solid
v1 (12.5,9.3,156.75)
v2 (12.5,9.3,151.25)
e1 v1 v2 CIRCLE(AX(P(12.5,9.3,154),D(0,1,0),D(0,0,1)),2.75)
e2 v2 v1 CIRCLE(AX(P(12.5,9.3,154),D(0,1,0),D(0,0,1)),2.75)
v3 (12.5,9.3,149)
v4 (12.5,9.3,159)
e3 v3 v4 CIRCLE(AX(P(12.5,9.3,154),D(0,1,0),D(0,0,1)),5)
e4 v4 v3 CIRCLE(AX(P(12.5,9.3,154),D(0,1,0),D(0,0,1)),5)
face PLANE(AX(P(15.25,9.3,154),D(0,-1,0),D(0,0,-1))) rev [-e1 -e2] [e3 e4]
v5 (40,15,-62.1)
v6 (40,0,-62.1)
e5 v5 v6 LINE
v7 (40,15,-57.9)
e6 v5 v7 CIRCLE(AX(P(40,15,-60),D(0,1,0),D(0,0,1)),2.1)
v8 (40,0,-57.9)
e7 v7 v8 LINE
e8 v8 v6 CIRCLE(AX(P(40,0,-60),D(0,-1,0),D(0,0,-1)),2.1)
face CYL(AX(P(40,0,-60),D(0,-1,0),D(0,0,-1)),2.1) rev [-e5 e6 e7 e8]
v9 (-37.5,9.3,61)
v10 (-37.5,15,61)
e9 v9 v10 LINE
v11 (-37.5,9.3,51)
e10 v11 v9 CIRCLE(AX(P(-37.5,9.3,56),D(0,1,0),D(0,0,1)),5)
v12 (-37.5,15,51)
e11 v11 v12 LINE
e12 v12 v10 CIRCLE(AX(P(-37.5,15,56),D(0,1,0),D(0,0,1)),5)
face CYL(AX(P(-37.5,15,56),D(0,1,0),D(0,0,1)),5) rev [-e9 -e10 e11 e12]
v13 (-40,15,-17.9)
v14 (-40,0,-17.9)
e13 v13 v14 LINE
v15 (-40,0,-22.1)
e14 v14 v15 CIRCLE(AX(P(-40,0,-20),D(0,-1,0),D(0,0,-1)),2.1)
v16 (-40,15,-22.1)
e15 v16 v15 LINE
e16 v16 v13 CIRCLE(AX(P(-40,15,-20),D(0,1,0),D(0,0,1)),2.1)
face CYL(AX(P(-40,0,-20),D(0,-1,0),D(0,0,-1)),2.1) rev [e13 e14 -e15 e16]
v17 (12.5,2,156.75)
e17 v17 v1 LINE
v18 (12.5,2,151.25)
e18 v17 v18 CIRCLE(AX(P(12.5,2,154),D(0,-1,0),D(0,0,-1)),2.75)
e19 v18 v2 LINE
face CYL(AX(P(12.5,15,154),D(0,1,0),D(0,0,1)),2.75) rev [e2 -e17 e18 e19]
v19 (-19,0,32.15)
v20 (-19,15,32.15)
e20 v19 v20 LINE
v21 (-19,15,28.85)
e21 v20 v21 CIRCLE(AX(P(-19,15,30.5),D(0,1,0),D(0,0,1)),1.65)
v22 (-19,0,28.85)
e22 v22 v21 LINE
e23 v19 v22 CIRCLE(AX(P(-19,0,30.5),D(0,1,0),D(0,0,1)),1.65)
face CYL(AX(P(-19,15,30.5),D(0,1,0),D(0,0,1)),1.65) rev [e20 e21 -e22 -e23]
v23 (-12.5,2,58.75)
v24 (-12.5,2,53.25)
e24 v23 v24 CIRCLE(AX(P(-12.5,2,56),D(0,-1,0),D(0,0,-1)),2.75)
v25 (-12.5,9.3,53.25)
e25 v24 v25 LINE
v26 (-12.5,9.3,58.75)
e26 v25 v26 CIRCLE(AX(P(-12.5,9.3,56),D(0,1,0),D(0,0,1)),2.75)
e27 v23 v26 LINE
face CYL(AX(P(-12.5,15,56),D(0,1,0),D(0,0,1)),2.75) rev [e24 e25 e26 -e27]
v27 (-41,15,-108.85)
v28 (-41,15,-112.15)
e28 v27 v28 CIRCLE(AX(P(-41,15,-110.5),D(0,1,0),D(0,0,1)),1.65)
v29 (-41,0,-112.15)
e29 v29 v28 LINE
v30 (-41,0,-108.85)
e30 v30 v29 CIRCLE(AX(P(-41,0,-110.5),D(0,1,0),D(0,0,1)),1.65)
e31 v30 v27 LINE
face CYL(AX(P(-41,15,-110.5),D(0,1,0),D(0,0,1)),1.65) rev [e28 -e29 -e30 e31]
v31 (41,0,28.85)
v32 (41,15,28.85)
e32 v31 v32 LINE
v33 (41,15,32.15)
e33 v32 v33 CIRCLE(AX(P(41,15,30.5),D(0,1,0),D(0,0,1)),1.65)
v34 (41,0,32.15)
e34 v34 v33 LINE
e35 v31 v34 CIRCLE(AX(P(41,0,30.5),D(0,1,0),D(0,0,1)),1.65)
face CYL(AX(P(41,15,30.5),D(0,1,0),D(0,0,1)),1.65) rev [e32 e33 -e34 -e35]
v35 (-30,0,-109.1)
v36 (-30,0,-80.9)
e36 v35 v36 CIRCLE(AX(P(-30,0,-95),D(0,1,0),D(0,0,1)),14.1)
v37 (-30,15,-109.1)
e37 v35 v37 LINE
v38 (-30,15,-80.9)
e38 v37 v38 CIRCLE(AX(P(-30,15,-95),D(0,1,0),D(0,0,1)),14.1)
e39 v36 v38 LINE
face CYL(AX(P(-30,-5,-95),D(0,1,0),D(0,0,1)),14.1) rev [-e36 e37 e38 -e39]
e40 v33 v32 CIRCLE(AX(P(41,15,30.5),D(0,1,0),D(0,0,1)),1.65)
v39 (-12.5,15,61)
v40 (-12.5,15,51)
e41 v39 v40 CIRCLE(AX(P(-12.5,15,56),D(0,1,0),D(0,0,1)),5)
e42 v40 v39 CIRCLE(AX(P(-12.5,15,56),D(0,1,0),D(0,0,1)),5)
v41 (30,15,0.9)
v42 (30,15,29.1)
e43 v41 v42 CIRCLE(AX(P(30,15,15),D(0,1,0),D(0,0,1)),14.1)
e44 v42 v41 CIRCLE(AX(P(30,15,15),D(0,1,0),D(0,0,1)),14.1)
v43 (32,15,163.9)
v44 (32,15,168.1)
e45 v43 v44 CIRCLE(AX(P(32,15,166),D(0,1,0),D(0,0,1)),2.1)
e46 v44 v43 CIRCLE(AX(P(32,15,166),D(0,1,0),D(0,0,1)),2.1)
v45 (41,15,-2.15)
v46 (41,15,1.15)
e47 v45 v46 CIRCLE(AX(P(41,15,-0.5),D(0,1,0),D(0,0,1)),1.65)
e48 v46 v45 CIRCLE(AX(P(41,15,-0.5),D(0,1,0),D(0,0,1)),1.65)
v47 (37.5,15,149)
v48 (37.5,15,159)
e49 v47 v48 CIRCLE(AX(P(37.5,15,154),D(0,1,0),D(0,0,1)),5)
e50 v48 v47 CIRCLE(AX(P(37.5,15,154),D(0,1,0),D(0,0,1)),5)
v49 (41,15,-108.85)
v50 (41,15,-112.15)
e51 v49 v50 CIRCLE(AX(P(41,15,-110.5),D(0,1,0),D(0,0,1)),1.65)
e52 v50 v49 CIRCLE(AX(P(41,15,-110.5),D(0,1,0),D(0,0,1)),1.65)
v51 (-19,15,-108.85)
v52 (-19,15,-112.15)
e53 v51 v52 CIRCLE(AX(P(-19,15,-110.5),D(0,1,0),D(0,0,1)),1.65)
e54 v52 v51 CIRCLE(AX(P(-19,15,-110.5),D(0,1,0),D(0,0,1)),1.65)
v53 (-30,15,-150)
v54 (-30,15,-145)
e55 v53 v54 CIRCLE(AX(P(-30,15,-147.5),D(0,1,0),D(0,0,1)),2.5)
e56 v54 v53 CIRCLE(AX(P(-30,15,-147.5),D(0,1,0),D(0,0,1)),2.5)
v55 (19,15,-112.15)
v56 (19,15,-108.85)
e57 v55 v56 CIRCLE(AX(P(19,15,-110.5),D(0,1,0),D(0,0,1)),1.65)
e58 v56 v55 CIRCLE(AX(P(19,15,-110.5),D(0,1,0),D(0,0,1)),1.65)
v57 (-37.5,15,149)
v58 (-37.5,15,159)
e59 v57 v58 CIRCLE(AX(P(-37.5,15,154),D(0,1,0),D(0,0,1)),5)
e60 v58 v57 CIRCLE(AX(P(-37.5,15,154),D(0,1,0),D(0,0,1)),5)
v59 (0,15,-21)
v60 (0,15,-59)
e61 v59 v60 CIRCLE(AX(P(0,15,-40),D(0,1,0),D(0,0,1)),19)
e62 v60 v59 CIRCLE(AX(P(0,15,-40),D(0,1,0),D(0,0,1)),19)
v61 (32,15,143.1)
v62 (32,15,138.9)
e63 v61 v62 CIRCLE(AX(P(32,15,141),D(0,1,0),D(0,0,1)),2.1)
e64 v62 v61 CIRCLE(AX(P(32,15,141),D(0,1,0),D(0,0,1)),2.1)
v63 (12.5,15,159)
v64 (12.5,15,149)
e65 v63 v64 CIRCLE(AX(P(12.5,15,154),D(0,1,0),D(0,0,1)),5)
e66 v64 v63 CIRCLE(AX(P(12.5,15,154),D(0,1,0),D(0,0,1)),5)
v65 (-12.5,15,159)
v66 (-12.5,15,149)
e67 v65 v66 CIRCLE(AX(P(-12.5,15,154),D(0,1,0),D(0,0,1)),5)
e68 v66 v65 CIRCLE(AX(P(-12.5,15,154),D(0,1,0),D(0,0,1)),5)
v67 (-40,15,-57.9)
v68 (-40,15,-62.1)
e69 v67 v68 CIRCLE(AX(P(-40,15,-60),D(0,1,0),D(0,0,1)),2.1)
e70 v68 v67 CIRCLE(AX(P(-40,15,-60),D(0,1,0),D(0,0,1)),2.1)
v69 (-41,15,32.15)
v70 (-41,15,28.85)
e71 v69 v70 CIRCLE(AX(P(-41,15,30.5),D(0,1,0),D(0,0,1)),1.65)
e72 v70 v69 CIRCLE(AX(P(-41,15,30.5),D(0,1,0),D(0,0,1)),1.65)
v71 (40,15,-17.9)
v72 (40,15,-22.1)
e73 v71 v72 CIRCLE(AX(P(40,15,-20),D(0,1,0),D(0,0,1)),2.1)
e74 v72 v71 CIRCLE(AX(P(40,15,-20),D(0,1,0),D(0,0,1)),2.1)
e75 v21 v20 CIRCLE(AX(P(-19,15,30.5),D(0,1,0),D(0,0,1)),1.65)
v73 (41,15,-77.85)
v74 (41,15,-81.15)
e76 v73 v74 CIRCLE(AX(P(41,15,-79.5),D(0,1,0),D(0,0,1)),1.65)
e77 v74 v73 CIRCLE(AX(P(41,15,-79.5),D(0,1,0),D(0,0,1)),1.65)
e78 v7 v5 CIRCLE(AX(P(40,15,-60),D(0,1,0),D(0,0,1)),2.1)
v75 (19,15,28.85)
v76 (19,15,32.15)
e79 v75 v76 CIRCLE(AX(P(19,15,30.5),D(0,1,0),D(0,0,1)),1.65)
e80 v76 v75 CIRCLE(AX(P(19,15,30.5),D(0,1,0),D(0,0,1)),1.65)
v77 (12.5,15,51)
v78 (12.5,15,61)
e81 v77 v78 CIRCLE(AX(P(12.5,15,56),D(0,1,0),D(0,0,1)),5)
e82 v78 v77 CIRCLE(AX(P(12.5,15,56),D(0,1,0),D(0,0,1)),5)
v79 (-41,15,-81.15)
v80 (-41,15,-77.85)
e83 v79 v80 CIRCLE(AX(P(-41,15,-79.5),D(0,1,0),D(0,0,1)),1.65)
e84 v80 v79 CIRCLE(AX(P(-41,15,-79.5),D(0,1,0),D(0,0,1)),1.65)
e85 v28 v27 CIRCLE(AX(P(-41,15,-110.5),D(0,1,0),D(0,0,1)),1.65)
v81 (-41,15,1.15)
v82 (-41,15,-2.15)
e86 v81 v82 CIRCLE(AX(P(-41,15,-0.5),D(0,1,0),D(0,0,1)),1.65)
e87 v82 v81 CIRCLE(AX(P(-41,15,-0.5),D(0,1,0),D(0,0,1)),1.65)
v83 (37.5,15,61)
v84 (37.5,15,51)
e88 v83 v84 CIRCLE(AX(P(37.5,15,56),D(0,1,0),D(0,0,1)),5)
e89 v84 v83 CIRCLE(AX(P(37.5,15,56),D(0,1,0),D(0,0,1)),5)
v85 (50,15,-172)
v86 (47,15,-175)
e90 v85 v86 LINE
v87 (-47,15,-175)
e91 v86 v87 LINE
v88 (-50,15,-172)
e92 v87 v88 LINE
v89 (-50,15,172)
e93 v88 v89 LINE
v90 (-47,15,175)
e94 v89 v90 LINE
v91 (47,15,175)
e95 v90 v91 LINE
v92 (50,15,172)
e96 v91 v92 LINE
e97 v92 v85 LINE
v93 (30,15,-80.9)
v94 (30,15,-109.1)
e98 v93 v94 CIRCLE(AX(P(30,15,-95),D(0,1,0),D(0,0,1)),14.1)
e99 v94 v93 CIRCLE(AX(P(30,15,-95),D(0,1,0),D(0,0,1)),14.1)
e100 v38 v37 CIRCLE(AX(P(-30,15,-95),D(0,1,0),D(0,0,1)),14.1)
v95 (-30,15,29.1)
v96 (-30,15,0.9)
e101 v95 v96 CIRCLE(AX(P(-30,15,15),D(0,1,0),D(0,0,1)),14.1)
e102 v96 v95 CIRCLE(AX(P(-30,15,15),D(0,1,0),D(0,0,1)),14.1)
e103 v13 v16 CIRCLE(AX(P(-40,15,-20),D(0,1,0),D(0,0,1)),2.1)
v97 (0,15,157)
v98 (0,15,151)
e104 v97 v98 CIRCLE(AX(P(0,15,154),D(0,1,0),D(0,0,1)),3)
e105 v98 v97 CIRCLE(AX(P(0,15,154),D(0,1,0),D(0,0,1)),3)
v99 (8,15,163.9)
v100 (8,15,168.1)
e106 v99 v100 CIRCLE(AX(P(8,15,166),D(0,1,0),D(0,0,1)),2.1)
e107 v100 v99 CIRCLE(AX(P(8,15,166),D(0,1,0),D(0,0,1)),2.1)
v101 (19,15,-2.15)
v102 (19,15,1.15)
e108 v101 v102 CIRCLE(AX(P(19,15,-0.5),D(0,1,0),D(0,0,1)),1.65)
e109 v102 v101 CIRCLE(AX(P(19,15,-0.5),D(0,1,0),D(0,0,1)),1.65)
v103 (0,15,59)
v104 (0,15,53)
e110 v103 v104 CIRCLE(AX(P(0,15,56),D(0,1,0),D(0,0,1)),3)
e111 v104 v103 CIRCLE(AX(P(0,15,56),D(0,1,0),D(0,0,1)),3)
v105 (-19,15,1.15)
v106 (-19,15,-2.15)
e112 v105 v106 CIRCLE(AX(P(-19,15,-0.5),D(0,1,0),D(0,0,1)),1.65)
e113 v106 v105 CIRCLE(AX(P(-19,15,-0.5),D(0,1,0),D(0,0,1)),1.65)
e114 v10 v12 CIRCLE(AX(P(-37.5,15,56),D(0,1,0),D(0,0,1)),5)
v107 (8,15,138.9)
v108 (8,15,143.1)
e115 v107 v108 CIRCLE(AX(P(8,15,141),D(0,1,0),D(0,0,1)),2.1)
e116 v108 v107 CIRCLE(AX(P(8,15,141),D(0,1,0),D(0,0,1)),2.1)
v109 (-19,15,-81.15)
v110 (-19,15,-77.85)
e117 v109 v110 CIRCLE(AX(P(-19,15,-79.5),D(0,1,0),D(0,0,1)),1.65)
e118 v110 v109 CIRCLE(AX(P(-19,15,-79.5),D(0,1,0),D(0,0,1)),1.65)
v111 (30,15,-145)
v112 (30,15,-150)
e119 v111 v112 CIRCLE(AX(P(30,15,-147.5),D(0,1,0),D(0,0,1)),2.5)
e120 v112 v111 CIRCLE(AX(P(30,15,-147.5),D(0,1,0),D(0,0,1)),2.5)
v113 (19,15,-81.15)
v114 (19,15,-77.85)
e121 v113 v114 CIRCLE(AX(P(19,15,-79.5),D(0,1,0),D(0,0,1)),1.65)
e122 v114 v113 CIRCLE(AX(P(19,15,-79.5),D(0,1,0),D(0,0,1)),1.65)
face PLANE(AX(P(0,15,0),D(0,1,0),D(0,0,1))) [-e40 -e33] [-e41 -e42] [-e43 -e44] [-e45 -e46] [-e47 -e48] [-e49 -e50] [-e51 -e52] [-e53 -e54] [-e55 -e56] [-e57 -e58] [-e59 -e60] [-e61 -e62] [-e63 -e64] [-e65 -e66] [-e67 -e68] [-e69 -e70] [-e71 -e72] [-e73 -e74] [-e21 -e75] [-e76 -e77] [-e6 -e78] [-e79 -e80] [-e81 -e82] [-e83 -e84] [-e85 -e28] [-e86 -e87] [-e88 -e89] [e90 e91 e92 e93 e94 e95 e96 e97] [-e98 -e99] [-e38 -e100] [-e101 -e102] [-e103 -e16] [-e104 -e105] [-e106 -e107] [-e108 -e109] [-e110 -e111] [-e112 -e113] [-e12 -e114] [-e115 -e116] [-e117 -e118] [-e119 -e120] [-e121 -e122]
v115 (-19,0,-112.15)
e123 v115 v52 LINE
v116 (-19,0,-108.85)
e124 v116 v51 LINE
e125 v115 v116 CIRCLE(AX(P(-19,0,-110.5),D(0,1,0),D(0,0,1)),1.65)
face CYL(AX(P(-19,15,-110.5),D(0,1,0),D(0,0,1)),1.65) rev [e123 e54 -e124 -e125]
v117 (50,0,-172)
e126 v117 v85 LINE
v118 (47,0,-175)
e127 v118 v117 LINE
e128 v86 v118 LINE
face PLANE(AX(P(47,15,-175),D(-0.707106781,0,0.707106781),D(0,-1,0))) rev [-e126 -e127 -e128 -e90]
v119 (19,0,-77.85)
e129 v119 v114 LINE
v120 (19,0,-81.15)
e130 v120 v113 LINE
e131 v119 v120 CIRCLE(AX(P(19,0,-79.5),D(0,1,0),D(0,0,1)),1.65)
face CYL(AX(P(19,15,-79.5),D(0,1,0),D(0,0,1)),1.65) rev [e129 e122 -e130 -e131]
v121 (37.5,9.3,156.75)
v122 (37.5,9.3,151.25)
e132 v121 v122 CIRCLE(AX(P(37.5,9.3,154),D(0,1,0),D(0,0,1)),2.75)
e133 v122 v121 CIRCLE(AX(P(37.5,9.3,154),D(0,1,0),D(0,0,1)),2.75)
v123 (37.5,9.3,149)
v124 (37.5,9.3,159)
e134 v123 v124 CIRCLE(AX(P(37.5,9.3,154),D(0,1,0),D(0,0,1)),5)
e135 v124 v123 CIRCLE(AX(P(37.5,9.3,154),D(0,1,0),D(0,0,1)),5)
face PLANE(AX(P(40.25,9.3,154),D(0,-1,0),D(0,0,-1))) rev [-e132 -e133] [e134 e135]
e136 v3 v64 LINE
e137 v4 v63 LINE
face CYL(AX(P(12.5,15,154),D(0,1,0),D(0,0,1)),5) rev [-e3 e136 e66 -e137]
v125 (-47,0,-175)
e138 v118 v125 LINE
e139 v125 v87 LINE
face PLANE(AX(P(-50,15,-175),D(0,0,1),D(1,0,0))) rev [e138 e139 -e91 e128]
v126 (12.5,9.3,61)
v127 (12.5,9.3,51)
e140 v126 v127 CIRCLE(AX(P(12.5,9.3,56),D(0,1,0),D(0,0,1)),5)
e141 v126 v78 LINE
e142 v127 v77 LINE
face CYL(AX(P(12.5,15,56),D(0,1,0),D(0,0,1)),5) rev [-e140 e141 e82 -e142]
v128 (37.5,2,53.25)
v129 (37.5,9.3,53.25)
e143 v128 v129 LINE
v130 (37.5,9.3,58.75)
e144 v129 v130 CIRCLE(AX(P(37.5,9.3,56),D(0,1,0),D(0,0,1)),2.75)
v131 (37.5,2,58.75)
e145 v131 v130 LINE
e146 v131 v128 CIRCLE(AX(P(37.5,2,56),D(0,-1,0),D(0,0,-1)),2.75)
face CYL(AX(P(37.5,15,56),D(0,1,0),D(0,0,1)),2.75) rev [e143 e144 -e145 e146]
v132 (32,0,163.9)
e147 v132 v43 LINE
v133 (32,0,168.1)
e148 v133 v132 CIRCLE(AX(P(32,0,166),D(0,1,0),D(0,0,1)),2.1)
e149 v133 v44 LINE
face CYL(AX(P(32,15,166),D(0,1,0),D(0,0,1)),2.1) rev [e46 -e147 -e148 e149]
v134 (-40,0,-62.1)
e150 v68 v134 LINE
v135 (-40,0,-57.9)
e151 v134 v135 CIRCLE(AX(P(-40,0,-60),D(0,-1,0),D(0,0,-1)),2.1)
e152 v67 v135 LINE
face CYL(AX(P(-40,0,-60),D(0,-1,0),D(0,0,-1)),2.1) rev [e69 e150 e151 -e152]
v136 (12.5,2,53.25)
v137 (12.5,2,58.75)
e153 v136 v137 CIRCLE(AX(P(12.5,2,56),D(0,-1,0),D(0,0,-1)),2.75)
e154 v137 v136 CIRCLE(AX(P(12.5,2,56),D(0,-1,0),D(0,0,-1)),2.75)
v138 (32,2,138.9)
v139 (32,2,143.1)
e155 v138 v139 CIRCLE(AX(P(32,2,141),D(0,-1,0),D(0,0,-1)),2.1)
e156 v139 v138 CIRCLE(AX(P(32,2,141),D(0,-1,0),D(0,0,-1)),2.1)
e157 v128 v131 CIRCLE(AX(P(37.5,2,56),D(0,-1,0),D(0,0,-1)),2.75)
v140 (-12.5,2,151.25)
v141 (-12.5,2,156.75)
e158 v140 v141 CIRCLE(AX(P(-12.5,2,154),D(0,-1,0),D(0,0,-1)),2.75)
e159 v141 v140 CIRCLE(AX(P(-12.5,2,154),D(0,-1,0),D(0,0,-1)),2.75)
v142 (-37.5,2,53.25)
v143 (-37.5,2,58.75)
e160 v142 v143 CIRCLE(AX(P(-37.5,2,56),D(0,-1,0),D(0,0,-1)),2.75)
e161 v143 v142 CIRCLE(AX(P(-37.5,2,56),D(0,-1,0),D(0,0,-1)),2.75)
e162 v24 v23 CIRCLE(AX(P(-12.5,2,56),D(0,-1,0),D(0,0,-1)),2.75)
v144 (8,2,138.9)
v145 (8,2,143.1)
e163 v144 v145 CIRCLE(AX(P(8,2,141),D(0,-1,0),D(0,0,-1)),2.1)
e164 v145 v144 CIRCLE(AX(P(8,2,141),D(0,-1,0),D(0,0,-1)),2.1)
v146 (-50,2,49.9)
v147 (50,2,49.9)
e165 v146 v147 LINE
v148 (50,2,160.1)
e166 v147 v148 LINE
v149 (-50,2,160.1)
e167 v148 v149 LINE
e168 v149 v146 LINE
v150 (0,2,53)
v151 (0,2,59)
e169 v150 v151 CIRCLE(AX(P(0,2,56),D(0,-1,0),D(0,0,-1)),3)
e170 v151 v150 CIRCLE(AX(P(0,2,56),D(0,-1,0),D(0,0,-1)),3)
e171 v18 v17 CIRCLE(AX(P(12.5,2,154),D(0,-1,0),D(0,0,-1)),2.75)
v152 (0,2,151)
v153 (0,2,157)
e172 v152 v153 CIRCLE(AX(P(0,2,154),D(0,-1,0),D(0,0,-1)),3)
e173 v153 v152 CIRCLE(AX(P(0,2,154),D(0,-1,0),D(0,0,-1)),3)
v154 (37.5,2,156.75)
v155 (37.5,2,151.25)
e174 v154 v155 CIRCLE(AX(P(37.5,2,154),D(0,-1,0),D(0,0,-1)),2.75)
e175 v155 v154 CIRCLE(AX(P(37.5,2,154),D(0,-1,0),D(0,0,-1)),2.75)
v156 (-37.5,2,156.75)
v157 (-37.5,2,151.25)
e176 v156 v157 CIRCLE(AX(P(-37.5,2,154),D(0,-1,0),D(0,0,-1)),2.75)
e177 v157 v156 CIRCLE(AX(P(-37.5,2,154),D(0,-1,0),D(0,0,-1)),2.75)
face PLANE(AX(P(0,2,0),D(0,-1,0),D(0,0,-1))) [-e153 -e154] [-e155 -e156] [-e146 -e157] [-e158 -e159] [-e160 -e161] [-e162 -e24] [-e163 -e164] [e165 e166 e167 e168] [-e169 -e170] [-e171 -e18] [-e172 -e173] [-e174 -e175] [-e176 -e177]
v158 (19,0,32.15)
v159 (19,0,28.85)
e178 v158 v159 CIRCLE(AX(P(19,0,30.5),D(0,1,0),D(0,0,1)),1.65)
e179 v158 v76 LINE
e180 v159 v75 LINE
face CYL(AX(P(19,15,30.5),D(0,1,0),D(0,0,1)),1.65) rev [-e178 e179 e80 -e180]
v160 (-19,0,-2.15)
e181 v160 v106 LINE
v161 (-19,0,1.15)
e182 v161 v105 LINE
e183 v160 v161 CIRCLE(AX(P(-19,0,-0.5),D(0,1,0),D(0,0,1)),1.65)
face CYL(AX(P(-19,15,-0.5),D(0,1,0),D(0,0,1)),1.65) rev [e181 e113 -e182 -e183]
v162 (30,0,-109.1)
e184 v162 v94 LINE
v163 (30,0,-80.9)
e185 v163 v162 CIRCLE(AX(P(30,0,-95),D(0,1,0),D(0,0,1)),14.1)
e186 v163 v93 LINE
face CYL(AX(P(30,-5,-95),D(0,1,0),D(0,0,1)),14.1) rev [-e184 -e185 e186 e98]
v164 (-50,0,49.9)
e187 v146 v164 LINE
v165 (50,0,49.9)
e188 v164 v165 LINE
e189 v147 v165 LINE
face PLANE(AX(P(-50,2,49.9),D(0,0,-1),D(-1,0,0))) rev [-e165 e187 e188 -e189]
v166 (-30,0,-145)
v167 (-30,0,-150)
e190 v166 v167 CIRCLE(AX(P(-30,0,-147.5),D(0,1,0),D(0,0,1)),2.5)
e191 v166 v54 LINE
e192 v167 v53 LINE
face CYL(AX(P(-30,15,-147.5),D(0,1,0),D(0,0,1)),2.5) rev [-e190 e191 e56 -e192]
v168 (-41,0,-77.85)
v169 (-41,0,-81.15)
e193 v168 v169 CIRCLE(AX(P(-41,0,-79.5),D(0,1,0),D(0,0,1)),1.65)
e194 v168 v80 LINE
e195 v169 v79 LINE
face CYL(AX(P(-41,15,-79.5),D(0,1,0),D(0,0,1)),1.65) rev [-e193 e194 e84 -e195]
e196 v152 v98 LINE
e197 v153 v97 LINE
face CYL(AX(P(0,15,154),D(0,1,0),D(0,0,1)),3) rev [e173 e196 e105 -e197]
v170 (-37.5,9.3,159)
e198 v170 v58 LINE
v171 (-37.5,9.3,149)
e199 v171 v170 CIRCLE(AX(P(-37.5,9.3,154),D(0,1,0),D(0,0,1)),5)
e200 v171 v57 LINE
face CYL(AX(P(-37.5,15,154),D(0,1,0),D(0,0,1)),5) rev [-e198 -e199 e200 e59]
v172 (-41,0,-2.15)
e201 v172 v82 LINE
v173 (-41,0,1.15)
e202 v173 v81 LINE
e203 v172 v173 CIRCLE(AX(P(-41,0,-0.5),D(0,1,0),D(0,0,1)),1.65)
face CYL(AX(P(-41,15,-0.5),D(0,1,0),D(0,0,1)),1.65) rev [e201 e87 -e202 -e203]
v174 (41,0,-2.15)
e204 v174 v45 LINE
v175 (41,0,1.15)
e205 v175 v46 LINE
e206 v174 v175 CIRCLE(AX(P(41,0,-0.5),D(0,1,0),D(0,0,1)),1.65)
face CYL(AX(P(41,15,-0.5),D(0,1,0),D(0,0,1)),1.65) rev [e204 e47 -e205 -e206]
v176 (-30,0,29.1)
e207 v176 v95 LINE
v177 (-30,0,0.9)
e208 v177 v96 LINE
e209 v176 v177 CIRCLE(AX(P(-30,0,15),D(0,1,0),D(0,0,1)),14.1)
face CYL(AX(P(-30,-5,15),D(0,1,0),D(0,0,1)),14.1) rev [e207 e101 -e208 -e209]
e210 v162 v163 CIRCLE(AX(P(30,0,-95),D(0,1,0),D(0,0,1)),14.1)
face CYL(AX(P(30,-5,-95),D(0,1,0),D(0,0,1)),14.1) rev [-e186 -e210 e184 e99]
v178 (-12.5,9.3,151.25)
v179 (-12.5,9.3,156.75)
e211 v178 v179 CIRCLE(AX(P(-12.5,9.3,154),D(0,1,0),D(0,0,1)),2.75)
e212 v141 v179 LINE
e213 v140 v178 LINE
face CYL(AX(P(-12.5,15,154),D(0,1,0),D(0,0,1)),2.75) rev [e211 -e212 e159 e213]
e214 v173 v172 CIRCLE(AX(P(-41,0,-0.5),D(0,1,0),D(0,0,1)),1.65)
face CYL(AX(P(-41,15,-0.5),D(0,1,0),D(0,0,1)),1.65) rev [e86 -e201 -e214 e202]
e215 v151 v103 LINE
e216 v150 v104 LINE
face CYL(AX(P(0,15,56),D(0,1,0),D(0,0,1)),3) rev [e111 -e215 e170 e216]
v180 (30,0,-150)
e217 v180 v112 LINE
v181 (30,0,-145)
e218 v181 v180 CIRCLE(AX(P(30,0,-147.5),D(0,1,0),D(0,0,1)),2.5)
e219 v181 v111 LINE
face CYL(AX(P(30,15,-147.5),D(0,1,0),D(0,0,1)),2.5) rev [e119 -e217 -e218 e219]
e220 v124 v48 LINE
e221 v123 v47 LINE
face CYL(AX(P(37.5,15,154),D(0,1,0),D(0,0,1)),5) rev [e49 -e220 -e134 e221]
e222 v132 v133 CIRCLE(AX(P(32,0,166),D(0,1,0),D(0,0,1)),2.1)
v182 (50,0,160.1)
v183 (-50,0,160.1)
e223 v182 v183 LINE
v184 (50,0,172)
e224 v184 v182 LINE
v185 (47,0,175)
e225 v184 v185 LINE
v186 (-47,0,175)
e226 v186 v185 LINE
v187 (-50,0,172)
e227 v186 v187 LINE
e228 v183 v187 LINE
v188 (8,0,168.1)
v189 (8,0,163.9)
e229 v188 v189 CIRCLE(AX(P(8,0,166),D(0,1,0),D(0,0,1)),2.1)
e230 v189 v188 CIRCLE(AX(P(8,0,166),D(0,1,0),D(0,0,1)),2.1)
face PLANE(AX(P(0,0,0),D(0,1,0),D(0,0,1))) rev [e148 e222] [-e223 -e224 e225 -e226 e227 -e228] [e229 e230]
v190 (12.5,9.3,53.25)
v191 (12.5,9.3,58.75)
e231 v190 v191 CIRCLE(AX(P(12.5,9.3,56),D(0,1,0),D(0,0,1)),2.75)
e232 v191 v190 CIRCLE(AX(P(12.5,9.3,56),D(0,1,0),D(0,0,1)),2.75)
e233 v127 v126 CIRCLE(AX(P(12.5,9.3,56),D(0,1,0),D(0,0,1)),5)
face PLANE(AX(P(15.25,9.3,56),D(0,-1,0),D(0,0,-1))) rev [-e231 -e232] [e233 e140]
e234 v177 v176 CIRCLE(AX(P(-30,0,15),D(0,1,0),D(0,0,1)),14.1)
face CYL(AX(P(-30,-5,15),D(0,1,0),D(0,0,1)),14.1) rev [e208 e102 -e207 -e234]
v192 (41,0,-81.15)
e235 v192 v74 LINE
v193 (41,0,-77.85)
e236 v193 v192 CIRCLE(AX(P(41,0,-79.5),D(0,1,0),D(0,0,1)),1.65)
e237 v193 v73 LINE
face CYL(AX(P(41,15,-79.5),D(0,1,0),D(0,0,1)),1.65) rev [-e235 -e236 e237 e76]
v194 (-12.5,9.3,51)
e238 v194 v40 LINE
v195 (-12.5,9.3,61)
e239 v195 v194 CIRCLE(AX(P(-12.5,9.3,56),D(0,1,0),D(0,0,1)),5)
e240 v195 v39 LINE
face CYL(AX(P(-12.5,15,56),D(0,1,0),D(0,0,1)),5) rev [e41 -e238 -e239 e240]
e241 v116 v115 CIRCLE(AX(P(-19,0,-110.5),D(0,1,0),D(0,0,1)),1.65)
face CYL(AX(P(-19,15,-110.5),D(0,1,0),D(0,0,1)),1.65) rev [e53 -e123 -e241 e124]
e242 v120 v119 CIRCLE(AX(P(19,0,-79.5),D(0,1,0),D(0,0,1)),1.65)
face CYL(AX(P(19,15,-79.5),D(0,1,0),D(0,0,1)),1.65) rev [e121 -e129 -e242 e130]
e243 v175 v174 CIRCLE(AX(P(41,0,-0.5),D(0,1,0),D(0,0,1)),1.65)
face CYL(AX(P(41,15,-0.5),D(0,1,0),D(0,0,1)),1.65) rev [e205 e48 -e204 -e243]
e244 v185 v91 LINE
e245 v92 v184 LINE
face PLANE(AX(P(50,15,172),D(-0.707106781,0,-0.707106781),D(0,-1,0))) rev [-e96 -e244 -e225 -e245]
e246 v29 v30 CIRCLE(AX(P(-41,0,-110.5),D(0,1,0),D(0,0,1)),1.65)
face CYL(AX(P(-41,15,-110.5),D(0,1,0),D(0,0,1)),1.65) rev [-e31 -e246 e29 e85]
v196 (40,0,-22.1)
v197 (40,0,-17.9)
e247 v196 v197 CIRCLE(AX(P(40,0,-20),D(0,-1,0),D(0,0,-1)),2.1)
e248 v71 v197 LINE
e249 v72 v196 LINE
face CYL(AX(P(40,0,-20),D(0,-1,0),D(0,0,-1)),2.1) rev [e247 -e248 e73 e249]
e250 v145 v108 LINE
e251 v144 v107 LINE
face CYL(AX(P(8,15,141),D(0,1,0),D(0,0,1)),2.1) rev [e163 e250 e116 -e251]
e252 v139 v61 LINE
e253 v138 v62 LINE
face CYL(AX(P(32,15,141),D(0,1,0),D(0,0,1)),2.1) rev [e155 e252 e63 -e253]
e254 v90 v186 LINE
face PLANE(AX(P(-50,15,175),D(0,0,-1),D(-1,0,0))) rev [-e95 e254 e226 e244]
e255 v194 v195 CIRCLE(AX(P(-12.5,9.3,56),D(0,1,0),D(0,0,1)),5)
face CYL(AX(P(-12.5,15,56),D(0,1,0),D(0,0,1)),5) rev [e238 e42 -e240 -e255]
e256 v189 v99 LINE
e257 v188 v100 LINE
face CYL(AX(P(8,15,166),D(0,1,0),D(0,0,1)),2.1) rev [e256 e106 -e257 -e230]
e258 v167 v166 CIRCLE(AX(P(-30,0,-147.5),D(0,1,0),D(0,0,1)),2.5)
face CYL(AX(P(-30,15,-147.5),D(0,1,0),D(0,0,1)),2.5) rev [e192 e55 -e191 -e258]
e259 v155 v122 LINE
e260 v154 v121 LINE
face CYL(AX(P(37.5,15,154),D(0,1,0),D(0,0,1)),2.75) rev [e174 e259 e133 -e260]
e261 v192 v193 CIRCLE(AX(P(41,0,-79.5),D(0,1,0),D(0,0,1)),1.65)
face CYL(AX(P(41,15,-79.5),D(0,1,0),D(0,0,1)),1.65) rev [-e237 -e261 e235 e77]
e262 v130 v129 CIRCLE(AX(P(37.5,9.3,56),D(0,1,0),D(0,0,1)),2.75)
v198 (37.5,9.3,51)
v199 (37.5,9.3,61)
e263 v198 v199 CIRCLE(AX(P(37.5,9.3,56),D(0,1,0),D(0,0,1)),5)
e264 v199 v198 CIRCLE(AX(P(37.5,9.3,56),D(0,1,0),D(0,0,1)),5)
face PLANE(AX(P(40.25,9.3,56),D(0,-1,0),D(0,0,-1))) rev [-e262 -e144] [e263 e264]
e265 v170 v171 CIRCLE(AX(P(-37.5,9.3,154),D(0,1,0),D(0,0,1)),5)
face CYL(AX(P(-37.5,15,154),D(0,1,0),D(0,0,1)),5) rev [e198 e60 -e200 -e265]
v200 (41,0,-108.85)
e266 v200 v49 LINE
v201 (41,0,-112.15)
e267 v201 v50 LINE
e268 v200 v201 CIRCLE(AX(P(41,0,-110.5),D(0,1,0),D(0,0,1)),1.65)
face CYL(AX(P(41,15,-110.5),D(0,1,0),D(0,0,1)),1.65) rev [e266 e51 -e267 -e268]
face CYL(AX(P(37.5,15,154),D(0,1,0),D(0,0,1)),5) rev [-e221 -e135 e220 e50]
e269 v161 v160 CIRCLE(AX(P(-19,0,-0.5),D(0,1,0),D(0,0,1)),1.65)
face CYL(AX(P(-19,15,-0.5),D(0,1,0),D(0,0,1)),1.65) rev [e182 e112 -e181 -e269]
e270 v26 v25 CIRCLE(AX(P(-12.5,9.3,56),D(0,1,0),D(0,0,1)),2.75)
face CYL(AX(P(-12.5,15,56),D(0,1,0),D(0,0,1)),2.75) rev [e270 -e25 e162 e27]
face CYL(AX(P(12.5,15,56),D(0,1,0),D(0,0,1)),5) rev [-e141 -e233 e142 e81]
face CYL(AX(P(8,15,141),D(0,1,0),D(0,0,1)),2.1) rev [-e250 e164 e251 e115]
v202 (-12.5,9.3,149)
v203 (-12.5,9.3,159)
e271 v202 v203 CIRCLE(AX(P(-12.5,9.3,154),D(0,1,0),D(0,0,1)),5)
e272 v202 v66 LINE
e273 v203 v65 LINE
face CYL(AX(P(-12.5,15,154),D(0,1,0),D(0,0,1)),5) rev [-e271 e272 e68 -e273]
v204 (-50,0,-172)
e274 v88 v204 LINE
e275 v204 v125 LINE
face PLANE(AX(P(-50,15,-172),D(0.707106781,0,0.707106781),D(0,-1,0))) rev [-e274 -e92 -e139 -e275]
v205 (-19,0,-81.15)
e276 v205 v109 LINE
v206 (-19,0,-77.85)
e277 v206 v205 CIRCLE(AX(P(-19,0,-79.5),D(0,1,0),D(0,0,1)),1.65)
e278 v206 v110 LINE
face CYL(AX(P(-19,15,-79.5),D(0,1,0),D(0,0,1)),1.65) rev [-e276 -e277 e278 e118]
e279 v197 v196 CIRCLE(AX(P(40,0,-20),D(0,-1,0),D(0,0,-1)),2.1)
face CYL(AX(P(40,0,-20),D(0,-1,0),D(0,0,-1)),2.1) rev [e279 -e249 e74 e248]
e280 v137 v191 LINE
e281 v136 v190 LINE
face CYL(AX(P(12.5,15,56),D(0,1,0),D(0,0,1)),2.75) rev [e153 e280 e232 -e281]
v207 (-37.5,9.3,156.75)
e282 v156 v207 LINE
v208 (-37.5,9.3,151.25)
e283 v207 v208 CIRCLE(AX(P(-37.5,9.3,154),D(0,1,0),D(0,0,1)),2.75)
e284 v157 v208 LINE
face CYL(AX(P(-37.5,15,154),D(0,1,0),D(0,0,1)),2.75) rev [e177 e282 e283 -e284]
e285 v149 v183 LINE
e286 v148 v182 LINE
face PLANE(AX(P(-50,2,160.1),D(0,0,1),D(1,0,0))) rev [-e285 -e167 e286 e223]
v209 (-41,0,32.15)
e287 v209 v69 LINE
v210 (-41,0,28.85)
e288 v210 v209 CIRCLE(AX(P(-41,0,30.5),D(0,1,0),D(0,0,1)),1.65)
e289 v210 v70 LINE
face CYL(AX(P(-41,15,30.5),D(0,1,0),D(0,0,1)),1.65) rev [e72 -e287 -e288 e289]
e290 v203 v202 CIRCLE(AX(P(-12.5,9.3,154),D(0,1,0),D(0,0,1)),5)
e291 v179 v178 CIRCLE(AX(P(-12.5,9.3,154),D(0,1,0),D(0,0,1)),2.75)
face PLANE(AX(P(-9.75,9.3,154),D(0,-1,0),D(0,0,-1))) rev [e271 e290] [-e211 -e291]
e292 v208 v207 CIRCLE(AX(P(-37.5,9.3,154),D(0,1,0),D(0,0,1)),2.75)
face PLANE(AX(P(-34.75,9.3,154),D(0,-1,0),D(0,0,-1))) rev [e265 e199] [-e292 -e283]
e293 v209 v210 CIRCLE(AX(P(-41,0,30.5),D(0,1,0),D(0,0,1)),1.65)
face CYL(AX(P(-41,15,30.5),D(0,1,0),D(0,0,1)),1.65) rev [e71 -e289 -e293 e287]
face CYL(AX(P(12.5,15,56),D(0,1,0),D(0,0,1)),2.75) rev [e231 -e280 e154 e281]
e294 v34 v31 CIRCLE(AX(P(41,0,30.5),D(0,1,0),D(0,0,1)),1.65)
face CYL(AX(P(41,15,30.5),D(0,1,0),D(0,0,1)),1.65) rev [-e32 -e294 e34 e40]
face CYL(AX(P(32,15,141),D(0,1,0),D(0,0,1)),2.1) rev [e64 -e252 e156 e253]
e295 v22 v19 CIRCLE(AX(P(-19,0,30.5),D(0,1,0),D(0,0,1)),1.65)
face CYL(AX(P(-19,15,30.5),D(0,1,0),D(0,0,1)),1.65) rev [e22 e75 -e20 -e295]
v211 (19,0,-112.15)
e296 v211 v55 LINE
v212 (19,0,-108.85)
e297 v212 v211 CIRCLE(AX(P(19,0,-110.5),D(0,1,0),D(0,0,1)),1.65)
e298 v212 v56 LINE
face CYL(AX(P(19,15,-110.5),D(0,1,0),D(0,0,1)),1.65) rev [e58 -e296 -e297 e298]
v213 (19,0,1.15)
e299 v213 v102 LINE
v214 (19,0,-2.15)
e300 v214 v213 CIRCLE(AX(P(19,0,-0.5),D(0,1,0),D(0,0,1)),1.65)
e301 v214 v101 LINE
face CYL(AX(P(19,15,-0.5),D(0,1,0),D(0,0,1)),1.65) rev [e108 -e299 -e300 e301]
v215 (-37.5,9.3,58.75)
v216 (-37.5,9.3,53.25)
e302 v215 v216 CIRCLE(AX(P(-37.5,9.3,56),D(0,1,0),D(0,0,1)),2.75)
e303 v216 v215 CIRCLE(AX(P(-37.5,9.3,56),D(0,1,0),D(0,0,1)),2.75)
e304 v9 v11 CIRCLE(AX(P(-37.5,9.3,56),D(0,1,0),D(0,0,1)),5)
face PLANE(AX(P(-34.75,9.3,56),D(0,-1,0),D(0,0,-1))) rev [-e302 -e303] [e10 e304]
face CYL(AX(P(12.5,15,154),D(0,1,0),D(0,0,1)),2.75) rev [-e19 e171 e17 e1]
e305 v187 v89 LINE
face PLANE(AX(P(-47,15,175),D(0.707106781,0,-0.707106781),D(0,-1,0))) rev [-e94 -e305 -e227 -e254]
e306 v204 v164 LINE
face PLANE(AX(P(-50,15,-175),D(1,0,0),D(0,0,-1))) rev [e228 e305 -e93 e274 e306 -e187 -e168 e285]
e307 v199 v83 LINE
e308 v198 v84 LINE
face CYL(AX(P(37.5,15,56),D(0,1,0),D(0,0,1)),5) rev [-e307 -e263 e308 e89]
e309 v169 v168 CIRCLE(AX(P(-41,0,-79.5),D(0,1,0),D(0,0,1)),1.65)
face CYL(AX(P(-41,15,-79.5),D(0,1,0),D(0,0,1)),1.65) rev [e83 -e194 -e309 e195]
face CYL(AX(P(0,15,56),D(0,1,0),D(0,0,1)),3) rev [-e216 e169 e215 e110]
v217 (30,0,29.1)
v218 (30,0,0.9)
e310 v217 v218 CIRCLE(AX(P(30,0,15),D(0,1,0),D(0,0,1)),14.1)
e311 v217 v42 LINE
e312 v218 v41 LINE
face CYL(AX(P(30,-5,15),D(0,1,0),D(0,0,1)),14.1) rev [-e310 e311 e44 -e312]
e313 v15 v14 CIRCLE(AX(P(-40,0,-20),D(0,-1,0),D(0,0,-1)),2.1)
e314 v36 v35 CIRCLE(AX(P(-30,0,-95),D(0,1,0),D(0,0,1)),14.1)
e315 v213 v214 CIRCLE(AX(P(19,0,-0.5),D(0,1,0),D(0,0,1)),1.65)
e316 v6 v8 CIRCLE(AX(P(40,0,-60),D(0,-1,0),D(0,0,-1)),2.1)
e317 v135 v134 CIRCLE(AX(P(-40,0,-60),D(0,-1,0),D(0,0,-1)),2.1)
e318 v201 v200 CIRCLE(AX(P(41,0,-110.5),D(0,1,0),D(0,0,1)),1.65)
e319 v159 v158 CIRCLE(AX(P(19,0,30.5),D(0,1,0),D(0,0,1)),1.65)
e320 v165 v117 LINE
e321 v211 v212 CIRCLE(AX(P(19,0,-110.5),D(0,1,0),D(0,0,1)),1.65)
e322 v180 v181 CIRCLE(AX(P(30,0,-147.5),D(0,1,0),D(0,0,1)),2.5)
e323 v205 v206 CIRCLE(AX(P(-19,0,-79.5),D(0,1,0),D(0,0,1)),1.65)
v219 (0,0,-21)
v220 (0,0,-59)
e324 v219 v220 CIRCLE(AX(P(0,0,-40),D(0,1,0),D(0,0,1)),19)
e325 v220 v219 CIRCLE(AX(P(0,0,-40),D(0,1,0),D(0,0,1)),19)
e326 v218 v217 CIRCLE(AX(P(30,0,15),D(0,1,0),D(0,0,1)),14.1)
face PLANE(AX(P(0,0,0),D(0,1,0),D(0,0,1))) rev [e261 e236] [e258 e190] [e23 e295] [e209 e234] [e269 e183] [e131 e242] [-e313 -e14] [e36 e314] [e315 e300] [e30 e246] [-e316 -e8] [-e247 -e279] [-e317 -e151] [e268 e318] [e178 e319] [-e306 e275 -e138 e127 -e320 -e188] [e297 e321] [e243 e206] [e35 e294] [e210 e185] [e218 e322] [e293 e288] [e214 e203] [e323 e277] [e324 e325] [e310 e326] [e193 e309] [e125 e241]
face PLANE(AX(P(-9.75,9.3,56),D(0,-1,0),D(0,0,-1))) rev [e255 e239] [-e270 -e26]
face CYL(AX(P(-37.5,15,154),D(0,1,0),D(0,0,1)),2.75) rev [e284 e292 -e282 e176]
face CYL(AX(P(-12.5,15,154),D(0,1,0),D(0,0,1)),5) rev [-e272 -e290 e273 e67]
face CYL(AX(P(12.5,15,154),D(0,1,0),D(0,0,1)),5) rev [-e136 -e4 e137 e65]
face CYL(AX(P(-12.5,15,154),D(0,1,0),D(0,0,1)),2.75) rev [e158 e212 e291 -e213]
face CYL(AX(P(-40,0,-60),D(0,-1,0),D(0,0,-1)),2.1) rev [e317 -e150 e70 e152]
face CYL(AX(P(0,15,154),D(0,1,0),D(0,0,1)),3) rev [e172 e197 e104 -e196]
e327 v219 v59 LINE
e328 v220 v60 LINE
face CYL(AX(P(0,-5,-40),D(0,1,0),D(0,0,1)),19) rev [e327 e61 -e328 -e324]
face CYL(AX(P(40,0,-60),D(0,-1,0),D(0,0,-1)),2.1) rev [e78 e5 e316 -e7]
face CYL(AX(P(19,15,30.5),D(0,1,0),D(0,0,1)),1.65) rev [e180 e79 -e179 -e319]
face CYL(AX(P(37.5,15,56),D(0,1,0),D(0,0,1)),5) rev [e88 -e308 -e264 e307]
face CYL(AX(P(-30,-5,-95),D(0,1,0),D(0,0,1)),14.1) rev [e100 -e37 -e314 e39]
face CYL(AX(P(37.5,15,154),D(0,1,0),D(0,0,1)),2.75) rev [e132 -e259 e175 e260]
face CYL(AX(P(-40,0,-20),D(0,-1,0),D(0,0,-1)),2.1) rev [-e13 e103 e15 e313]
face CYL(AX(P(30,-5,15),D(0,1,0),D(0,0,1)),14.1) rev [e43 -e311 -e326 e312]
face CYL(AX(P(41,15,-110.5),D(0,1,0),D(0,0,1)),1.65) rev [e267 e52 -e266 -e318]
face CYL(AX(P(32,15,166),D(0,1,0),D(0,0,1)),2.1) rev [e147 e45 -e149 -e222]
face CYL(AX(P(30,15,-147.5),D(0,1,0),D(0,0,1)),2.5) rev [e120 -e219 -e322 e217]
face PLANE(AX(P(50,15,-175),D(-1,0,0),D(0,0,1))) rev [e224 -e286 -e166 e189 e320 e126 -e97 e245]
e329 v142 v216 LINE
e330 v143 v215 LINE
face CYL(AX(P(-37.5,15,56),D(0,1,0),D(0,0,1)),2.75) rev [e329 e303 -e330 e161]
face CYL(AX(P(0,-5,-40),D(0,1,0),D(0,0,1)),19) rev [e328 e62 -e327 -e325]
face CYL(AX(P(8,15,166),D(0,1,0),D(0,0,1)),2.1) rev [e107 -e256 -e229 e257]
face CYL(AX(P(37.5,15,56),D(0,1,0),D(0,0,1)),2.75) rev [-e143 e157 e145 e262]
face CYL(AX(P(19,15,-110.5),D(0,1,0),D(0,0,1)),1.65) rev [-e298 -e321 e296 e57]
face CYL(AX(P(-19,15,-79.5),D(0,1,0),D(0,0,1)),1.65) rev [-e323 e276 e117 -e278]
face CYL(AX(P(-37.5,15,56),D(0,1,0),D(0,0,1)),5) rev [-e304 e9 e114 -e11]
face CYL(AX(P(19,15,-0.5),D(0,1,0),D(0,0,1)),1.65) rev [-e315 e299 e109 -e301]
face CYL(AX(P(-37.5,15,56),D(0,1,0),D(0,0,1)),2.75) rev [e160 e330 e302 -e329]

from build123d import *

# Parameters (mm, degrees)
SKETCH_1_W                = 100
SKETCH_1_H                = 350
EXTRUDE_1_DEPTH           = 15
SKETCH_3_W                = 100
SKETCH_3_H                = 110.2
CUT_EXTRUDE_1_DEPTH       = 2
HOLE_WIZARD_1_D           = 5.5
HOLE_WIZARD_1_DEPTH       = 15
HOLE_WIZARD_1_CBORE_D     = 10
HOLE_WIZARD_1_CBORE_DEPTH = 5.7
HOLE_WIZARD_1_TIP         = 1.652366702
MM_1_D                    = 6
MM_1_DEPTH                = 15
MM_1_TIP                  = 1.802581857
SKETCH_8_R                = 19
CUT_EXTRUDE_2_DEPTH       = 20
CHAMFER_1_SIZE            = 3
SKETCH_9_R                = 14.1
CUT_EXTRUDE_3_DEPTH       = 20
MM_2_D                    = 5
MM_2_DEPTH                = 20
MM_2_TIP                  = 1.502151548
HOLE_WIZARD_M5_1_D        = 4.2
HOLE_WIZARD_M5_1_DEPTH    = 20
HOLE_WIZARD_M5_1_TIP      = 1.2618073
HOLE_WIZARD_M4_1_D        = 3.3
HOLE_WIZARD_M4_1_DEPTH    = 32
HOLE_WIZARD_M4_1_TIP      = 0.991420021
HOLE_WIZARD_M5_2_D        = 4.2
HOLE_WIZARD_M5_2_DEPTH    = 20
HOLE_WIZARD_M5_2_TIP      = 1.2618073


with BuildPart() as part:
    # 草图1 → 凸台-拉伸1 (new body)
    with BuildSketch(Plane(origin=(0, 0, 0), x_dir=(1, 0, 0), z_dir=(0, 1, 0))):
        Rectangle(SKETCH_1_W, SKETCH_1_H)
    extrude(amount=EXTRUDE_1_DEPTH)

    # 草图3 → 切除-拉伸1 (cut)
    with BuildSketch(Plane.XZ):
        with Locations((0, 105)):
            Rectangle(SKETCH_3_W, SKETCH_3_H)
    extrude(amount=-CUT_EXTRUDE_1_DEPTH, mode=Mode.SUBTRACT)

    # 打孔尺寸(%根据)内六角圆柱头螺钉的类型1
    with Locations(Plane(origin=(0, 15, 0), x_dir=(1, 0, 0), z_dir=(0, 1, 0))):
        with Locations((-37.5, -154), (-12.5, -154), (12.5, -154), (37.5, -154), (-37.5, -56), (-12.5, -56), (12.5, -56), (37.5, -56)):
            CounterBoreHole(HOLE_WIZARD_1_D / 2, HOLE_WIZARD_1_CBORE_D / 2, HOLE_WIZARD_1_CBORE_DEPTH, depth=HOLE_WIZARD_1_DEPTH)
            with Locations((0, 0, -(HOLE_WIZARD_1_DEPTH + HOLE_WIZARD_1_TIP / 2))):  # 118° drill point
                Cone(0, HOLE_WIZARD_1_D / 2, HOLE_WIZARD_1_TIP, mode=Mode.SUBTRACT)

    # 大小mm 暗销孔1
    with Locations(Plane(origin=(0, 15, 0), x_dir=(1, 0, 0), z_dir=(0, 1, 0))):
        with Locations((0, -154), (0, -56)):
            Hole(MM_1_D / 2, depth=MM_1_DEPTH)
            with Locations((0, 0, -(MM_1_DEPTH + MM_1_TIP / 2))):  # 118° drill point
                Cone(0, MM_1_D / 2, MM_1_TIP, mode=Mode.SUBTRACT)

    # 草图8 → 切除-拉伸2 (cut)
    with BuildSketch(Plane(origin=(0, 15, 0), x_dir=(1, 0, 0), z_dir=(0, 1, 0))):
        with Locations(Location((0, 40, 0), (0, 0, 270))):
            Circle(SKETCH_8_R)
    extrude(amount=-CUT_EXTRUDE_2_DEPTH, mode=Mode.SUBTRACT)

    # 倒角1
    chamfer_1_edges = [part.edges().sort_by_distance(p)[0] for p in [
        (50, 7.5, 175),
        (-50, 7.5, 175),
        (-50, 7.5, -175),
        (50, 7.5, -175),
    ]]
    chamfer(chamfer_1_edges, length=CHAMFER_1_SIZE)

    # 草图9 → 切除-拉伸3 (cut)
    with BuildSketch(Plane(origin=(0, 15, 0), x_dir=(1, 0, 0), z_dir=(0, 1, 0))):
        with Locations(Location((30, -15, 0), (0, 0, 270))):
            Circle(SKETCH_9_R)
        with Locations(Location((30, 95, 0), (0, 0, 270))):
            Circle(SKETCH_9_R)
        with Locations(Location((-30, -15, 0), (0, 0, 270))):
            Circle(SKETCH_9_R)
        with Locations(Location((-30, 95, 0), (0, 0, 270))):
            Circle(SKETCH_9_R)
    extrude(amount=-CUT_EXTRUDE_3_DEPTH, mode=Mode.SUBTRACT)

    # 大小mm 暗销孔2
    with Locations(Plane(origin=(0, 15, 0), x_dir=(1, 0, 0), z_dir=(0, 1, 0))):
        with Locations((29.999999986, 147.499999994), (-30.000000014, 147.499999994)):
            Hole(MM_2_D / 2, depth=MM_2_DEPTH)
            with Locations((0, 0, -(MM_2_DEPTH + MM_2_TIP / 2))):  # 118° drill point
                Cone(0, MM_2_D / 2, MM_2_TIP, mode=Mode.SUBTRACT)

    # M5 螺纹孔1
    with Locations(Plane(origin=(0, 0, 0), x_dir=(-1, 0, 0), z_dir=(0, -1, 0))):
        with Locations((40, 19.999999999), (-40, 19.999999999), (40, 59.999999999), (-40, 59.999999999)):
            Hole(HOLE_WIZARD_M5_1_D / 2, depth=HOLE_WIZARD_M5_1_DEPTH)
            with Locations((0, 0, -(HOLE_WIZARD_M5_1_DEPTH + HOLE_WIZARD_M5_1_TIP / 2))):  # 118° drill point
                Cone(0, HOLE_WIZARD_M5_1_D / 2, HOLE_WIZARD_M5_1_TIP, mode=Mode.SUBTRACT)

    # M4 螺纹孔1
    with Locations(Plane(origin=(0, 15, 0), x_dir=(1, 0, 0), z_dir=(0, 1, 0))):
        with Locations((41, -30.5), (19, -30.5), (41, 0.5), (19, 0.5), (-19, -30.5), (-41, -30.5), (-19, 0.5), (-41, 0.5), (41, 79.5), (19, 79.5), (41, 110.5), (19, 110.5), (-19, 79.5), (-41, 79.5), (-19, 110.5), (-41, 110.5)):
            Hole(HOLE_WIZARD_M4_1_D / 2, depth=HOLE_WIZARD_M4_1_DEPTH)
            with Locations((0, 0, -(HOLE_WIZARD_M4_1_DEPTH + HOLE_WIZARD_M4_1_TIP / 2))):  # 118° drill point
                Cone(0, HOLE_WIZARD_M4_1_D / 2, HOLE_WIZARD_M4_1_TIP, mode=Mode.SUBTRACT)

    # M5 螺纹孔2
    with Locations(Plane(origin=(0, 15, 0), x_dir=(1, 0, 0), z_dir=(0, 1, 0))):
        with Locations((8, -141), (32, -141), (8, -166), (32, -166)):
            Hole(HOLE_WIZARD_M5_2_D / 2, depth=HOLE_WIZARD_M5_2_DEPTH)
            with Locations((0, 0, -(HOLE_WIZARD_M5_2_DEPTH + HOLE_WIZARD_M5_2_TIP / 2))):  # 118° drill point
                Cone(0, HOLE_WIZARD_M5_2_D / 2, HOLE_WIZARD_M5_2_TIP, mode=Mode.SUBTRACT)


solid = part.part
